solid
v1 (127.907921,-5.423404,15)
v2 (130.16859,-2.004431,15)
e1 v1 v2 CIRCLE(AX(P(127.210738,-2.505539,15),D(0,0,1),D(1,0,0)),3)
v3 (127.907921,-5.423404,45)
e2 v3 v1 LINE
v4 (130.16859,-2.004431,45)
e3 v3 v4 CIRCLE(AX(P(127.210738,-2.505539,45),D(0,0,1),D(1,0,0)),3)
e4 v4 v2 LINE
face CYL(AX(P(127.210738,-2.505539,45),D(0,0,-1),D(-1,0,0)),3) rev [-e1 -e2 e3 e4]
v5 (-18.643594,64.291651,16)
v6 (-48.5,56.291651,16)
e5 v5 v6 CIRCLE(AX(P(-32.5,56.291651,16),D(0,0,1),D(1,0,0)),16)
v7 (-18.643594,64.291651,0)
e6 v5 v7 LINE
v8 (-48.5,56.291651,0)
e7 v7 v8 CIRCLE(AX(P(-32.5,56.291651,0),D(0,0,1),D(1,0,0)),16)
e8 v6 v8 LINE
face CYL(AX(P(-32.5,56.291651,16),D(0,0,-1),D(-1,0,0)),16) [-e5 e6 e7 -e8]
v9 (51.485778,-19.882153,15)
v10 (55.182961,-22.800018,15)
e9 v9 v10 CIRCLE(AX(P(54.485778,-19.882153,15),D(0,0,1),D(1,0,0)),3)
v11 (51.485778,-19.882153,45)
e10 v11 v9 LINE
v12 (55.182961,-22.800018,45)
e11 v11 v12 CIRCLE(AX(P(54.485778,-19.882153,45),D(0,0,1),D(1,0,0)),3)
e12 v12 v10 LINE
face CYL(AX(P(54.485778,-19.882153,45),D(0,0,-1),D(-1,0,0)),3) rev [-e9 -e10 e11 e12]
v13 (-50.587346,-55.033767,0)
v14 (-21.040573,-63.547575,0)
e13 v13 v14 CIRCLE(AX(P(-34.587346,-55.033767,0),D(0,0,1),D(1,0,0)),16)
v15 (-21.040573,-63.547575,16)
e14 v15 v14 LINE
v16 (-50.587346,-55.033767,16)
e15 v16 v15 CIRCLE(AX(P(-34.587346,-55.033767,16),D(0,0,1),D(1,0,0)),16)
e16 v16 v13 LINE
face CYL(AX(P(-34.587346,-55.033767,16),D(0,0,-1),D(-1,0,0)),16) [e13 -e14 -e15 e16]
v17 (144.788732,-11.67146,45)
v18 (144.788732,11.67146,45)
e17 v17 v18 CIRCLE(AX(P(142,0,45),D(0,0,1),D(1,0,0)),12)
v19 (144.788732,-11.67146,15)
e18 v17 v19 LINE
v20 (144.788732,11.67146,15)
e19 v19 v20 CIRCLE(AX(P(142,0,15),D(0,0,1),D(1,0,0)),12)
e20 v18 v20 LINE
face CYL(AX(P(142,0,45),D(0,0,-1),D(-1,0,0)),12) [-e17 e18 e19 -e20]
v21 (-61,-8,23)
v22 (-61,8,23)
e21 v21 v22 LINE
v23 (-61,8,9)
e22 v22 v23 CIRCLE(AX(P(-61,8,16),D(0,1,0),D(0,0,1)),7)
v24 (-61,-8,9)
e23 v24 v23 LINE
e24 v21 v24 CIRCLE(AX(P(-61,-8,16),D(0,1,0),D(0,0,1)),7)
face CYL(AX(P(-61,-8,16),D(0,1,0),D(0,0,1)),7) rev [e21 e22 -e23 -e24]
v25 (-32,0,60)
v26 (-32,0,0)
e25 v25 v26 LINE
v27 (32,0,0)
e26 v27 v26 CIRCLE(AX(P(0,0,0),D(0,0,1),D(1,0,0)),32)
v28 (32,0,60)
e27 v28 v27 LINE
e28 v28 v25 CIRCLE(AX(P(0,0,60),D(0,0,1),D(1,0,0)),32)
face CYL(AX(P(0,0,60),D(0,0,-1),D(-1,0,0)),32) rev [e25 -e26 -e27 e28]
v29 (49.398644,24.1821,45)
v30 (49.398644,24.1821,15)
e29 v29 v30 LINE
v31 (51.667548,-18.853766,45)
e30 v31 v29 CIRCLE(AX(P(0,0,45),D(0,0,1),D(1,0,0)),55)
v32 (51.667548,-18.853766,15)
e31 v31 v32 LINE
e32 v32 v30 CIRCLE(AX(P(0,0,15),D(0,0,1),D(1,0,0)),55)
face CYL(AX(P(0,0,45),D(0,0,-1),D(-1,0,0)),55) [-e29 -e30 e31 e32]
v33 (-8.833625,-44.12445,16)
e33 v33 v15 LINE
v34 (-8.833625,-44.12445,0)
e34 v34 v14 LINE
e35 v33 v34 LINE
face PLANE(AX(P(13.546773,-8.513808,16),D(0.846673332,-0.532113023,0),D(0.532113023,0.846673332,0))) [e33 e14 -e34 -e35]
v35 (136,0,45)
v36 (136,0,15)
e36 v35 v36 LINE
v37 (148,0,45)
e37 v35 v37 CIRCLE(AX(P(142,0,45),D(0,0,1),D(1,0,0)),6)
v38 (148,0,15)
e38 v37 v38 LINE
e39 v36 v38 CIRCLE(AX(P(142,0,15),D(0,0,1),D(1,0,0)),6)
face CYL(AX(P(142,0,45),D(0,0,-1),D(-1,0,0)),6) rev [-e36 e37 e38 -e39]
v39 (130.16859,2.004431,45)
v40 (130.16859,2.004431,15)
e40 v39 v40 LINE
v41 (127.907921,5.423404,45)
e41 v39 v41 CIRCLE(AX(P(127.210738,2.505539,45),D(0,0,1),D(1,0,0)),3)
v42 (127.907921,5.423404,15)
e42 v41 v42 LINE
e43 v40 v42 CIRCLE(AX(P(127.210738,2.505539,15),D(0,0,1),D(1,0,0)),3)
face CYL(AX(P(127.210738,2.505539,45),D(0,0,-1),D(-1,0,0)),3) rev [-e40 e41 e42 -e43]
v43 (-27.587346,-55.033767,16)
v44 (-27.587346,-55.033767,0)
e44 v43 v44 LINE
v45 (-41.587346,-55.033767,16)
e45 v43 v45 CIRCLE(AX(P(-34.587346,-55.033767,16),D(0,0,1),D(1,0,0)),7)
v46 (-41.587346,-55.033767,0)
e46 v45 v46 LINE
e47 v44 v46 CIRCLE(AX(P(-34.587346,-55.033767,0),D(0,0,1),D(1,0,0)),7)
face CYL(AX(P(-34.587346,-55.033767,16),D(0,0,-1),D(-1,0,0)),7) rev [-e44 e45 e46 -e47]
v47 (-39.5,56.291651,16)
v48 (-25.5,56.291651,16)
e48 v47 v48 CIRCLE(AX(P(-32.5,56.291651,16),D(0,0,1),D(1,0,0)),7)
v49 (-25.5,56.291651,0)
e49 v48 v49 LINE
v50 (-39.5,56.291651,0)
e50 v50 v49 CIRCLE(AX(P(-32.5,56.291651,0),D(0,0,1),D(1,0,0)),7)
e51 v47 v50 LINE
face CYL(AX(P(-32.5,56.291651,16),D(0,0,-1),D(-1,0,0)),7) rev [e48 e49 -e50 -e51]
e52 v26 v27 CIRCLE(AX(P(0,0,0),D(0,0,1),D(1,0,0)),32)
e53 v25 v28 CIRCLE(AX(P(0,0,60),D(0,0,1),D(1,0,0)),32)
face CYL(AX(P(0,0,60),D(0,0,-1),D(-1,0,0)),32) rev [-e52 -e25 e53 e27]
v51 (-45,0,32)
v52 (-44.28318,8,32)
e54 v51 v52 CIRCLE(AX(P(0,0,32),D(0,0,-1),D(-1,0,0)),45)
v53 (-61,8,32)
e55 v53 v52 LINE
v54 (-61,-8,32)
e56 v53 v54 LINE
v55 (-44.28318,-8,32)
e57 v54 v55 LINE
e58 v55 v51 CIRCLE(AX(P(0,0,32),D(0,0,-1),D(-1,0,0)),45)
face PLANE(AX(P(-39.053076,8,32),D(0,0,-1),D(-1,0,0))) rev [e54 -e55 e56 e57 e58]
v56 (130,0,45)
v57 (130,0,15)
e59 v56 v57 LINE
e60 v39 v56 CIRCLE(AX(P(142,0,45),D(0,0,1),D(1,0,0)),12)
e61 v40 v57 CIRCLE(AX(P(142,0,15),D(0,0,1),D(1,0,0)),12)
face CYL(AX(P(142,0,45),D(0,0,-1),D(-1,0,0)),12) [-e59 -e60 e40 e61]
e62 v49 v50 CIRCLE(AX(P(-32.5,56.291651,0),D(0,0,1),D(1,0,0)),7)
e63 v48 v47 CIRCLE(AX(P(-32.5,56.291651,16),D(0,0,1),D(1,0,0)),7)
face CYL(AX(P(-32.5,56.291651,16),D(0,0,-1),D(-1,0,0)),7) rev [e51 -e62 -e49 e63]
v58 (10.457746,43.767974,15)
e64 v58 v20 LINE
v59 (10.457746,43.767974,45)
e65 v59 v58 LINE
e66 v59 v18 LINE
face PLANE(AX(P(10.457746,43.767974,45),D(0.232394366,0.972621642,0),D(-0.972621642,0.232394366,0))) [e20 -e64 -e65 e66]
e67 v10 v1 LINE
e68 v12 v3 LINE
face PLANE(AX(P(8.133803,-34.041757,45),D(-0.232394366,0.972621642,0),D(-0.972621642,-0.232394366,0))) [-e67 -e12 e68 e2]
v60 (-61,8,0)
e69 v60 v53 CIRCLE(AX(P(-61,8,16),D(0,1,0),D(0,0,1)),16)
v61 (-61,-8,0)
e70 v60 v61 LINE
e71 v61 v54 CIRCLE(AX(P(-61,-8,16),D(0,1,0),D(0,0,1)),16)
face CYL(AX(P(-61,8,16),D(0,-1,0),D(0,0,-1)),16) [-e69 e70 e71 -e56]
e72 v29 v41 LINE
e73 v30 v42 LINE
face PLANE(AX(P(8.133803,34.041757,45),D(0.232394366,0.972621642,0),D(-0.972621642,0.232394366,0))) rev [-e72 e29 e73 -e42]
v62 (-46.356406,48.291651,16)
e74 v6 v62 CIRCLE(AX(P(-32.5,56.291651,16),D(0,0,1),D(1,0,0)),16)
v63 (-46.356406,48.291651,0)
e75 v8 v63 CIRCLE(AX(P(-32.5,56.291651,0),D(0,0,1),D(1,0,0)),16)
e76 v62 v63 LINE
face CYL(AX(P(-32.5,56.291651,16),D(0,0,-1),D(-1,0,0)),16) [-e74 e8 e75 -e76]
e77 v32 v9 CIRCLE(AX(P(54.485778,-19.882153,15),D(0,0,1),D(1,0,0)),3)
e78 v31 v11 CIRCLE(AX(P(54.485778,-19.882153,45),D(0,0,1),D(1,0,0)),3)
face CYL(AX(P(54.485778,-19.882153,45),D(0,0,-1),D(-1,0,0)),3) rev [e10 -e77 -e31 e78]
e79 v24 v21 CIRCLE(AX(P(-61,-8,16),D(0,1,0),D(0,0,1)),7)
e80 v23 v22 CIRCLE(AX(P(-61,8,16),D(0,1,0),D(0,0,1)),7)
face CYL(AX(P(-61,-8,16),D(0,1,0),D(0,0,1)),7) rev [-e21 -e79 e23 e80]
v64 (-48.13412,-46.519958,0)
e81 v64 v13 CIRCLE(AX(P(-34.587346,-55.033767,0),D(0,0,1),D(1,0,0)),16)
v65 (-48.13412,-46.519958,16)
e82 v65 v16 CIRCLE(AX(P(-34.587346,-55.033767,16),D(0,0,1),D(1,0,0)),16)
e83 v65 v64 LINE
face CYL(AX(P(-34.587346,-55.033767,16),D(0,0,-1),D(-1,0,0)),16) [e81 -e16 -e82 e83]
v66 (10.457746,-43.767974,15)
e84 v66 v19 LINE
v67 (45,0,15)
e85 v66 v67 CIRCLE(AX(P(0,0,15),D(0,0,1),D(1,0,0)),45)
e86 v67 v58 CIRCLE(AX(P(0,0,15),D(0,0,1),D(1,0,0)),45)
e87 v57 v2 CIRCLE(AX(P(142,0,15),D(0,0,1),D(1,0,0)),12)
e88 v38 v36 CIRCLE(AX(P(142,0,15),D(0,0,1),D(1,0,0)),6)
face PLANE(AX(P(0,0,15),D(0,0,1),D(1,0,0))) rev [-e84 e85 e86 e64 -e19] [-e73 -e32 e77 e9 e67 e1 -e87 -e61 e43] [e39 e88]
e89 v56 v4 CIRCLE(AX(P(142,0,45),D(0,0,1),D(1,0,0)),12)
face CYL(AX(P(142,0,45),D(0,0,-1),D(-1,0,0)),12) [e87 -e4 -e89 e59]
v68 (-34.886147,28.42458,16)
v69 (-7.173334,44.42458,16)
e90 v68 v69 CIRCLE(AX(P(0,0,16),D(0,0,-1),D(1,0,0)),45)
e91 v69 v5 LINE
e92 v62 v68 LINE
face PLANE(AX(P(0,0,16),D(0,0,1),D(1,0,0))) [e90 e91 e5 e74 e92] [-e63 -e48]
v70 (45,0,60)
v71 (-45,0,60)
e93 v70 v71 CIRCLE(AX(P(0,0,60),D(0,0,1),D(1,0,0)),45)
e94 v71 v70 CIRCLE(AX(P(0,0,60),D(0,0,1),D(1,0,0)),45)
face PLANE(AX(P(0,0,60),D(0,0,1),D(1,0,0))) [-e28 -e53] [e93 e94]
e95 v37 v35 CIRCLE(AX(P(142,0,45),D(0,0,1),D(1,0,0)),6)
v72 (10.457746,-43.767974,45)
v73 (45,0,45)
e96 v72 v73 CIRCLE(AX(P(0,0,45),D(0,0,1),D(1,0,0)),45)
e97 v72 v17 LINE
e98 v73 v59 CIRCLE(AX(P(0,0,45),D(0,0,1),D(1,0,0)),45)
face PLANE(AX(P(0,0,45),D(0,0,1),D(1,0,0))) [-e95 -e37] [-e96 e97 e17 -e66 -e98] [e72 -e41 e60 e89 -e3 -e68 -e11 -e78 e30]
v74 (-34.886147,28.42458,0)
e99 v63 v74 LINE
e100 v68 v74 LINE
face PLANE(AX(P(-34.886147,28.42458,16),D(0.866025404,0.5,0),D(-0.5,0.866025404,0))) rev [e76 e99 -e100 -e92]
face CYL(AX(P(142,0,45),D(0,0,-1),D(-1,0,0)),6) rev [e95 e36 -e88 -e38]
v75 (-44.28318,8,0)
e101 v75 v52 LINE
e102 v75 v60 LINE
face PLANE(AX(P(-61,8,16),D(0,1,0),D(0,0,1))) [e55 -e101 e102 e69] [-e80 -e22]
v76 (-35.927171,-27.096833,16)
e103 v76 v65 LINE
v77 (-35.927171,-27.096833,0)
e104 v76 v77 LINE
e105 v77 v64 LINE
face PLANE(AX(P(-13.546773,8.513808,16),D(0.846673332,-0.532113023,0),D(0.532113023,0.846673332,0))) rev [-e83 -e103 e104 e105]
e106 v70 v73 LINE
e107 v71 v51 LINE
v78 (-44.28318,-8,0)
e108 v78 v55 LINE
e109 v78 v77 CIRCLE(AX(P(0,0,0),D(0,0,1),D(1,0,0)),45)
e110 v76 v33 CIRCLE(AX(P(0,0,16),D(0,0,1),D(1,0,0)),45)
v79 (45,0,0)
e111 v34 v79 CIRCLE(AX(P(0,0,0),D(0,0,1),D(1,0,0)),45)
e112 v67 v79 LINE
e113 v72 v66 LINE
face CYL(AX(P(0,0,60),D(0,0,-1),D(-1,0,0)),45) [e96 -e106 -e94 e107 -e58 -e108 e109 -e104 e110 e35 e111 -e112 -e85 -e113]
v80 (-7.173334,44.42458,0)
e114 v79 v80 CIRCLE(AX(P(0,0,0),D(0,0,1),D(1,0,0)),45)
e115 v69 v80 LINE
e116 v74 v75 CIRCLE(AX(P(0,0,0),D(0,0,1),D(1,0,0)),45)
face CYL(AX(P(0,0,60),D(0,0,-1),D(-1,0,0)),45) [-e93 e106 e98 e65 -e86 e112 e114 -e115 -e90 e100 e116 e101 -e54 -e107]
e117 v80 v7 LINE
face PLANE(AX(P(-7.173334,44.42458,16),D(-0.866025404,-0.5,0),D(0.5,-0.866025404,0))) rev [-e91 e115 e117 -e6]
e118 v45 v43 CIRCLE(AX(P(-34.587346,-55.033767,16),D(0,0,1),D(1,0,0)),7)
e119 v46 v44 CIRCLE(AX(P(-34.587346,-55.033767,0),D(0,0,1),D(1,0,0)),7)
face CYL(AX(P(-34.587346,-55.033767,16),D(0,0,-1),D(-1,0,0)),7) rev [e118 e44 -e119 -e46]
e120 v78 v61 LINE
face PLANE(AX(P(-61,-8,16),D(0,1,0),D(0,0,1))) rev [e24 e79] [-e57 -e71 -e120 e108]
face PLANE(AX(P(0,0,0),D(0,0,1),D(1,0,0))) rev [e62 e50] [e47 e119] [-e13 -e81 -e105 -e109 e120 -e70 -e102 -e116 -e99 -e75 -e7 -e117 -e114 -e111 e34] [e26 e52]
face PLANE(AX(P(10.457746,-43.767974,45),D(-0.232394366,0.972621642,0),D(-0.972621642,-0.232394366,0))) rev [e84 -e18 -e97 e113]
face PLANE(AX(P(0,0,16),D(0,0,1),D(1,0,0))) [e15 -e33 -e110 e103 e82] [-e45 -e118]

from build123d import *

# Parameters (mm, degrees)
HUB_PROFILE_90X_64_R   = 45
HUB_PROFILE_90X_64_R_2 = 32
HUB_90X_64_DEPTH       = 60
ARM_WEB_PROFILE_R      = 6
WEBBED_ARM_DEPTH       = 15
LUG_A_PROFILE_R        = 7
LUG_A_30DEG_DEPTH      = 16
LUG_B_PROFILE_R        = 7
LUG_B_30DEG_DEPTH      = 16
LUG_BOSS_DEPTH         = 8
LUG_HOLE_PROFILE_R     = 7
LUG_THROUGH_HOLE_DEPTH = 16


with BuildPart() as part:
    # Hub Profile Ø90xØ64 → Hub Ø90xØ64 (new body)
    with BuildSketch(Plane.XY):
        Circle(HUB_PROFILE_90X_64_R)
        Circle(HUB_PROFILE_90X_64_R_2, mode=Mode.SUBTRACT)
    extrude(amount=HUB_90X_64_DEPTH)

    # Arm Web Profile → Webbed Arm (add, symmetric)
    with BuildSketch(Plane.XY.offset(30)):
        with BuildLine():
            Line((10.457746479, -43.767973892), (144.788732394, -11.671459704))
            ThreePointArc((144.788732394, -11.671459704), (154, 0), (144.788732394, 11.671459704))
            Line((144.788732394, 11.671459704), (10.457746479, 43.767973892))
            ThreePointArc((10.457746479, 43.767973892), (45, 0), (10.457746479, -43.767973892))
        make_face()
        with Locations((142, 0)):
            Circle(ARM_WEB_PROFILE_R, mode=Mode.SUBTRACT)
        with BuildLine():
            ThreePointArc((127.907920927, -5.423403672), (129.71316959, -4.160179273), (130.168590262, -2.004430997))
            ThreePointArc((130.168590262, -2.004430997), (130, 0), (130.168590262, 2.004430997))
            ThreePointArc((130.168590262, 2.004430997), (129.71316959, 4.160179273), (127.907920927, 5.423403672))
            Line((127.907920927, 5.423403672), (49.398644334, 24.182099536))
            ThreePointArc((49.398644334, 24.182099536), (54.923721956, 2.89564613), (51.667548043, -18.853765651))
            ThreePointArc((51.667548043, -18.853765651), (52.245702855, -21.877663737), (55.182961035, -22.800017794))
            Line((55.182961035, -22.800017794), (127.907920927, -5.423403672))
        make_face(mode=Mode.SUBTRACT)
    extrude(amount=WEBBED_ARM_DEPTH, both=True)

    # Lug A Profile → Lug A 30deg (add)
    with BuildSketch(Plane.XY):
        with BuildLine():
            Line((-34.886147305, 28.424579613), (-46.356406461, 48.291651246))
            ThreePointArc((-46.356406461, 48.291651246), (-40.5, 70.148057707), (-18.643593539, 64.291651246))
            Line((-18.643593539, 64.291651246), (-7.173334384, 44.424579613))
            ThreePointArc((-7.173334384, 44.424579613), (-22.5, 38.97114317), (-34.886147305, 28.424579613))
        make_face()
        with Locations((-32.5, 56.291651246)):
            Circle(LUG_A_PROFILE_R, mode=Mode.SUBTRACT)
    extrude(amount=LUG_A_30DEG_DEPTH)

    # Lug B Profile → Lug B 30deg (add)
    with BuildSketch(Plane.XY):
        with BuildLine():
            ThreePointArc((-8.833624625, -44.124449866), (-23.945086023, -38.100299938), (-35.927171248, -27.096833139))
            Line((-35.927171248, -27.096833139), (-48.134119789, -46.519958213))
            ThreePointArc((-48.134119789, -46.519958213), (-43.101154841, -68.580539888), (-21.040573166, -63.547574941))
            Line((-21.040573166, -63.547574941), (-8.833624625, -44.124449866))
        make_face()
        with Locations((-34.587346477, -55.033766577)):
            Circle(LUG_B_PROFILE_R, mode=Mode.SUBTRACT)
    extrude(amount=LUG_B_30DEG_DEPTH)

    # Lug Boss Profile → Lug Boss (add, symmetric)
    with BuildSketch(Plane(origin=(0, 0, 0), x_dir=(1, 0, 0), z_dir=(0, 1, 0))):
        with BuildLine():
            Line((-61, 0), (-45, 0))
            Line((-45, 0), (-39.05307602, 0))
            Line((-39.05307602, 0), (-39.05307602, -32))
            Line((-39.05307602, -32), (-45, -32))
            Line((-45, -32), (-61, -32))
            ThreePointArc((-61, -32), (-77, -16), (-61, 0))
        make_face()
    extrude(amount=LUG_BOSS_DEPTH, both=True)

    # Lug Hole Profile → Lug Through Hole (cut)
    with BuildSketch(Plane(origin=(0, 8, 0), x_dir=(1, 0, 0), z_dir=(0, 1, 0))):
        with Locations(Location((-61, -16, 0), (0, 0, 270))):
            Circle(LUG_HOLE_PROFILE_R)
    extrude(amount=-LUG_THROUGH_HOLE_DEPTH, mode=Mode.SUBTRACT)


solid = part.part
